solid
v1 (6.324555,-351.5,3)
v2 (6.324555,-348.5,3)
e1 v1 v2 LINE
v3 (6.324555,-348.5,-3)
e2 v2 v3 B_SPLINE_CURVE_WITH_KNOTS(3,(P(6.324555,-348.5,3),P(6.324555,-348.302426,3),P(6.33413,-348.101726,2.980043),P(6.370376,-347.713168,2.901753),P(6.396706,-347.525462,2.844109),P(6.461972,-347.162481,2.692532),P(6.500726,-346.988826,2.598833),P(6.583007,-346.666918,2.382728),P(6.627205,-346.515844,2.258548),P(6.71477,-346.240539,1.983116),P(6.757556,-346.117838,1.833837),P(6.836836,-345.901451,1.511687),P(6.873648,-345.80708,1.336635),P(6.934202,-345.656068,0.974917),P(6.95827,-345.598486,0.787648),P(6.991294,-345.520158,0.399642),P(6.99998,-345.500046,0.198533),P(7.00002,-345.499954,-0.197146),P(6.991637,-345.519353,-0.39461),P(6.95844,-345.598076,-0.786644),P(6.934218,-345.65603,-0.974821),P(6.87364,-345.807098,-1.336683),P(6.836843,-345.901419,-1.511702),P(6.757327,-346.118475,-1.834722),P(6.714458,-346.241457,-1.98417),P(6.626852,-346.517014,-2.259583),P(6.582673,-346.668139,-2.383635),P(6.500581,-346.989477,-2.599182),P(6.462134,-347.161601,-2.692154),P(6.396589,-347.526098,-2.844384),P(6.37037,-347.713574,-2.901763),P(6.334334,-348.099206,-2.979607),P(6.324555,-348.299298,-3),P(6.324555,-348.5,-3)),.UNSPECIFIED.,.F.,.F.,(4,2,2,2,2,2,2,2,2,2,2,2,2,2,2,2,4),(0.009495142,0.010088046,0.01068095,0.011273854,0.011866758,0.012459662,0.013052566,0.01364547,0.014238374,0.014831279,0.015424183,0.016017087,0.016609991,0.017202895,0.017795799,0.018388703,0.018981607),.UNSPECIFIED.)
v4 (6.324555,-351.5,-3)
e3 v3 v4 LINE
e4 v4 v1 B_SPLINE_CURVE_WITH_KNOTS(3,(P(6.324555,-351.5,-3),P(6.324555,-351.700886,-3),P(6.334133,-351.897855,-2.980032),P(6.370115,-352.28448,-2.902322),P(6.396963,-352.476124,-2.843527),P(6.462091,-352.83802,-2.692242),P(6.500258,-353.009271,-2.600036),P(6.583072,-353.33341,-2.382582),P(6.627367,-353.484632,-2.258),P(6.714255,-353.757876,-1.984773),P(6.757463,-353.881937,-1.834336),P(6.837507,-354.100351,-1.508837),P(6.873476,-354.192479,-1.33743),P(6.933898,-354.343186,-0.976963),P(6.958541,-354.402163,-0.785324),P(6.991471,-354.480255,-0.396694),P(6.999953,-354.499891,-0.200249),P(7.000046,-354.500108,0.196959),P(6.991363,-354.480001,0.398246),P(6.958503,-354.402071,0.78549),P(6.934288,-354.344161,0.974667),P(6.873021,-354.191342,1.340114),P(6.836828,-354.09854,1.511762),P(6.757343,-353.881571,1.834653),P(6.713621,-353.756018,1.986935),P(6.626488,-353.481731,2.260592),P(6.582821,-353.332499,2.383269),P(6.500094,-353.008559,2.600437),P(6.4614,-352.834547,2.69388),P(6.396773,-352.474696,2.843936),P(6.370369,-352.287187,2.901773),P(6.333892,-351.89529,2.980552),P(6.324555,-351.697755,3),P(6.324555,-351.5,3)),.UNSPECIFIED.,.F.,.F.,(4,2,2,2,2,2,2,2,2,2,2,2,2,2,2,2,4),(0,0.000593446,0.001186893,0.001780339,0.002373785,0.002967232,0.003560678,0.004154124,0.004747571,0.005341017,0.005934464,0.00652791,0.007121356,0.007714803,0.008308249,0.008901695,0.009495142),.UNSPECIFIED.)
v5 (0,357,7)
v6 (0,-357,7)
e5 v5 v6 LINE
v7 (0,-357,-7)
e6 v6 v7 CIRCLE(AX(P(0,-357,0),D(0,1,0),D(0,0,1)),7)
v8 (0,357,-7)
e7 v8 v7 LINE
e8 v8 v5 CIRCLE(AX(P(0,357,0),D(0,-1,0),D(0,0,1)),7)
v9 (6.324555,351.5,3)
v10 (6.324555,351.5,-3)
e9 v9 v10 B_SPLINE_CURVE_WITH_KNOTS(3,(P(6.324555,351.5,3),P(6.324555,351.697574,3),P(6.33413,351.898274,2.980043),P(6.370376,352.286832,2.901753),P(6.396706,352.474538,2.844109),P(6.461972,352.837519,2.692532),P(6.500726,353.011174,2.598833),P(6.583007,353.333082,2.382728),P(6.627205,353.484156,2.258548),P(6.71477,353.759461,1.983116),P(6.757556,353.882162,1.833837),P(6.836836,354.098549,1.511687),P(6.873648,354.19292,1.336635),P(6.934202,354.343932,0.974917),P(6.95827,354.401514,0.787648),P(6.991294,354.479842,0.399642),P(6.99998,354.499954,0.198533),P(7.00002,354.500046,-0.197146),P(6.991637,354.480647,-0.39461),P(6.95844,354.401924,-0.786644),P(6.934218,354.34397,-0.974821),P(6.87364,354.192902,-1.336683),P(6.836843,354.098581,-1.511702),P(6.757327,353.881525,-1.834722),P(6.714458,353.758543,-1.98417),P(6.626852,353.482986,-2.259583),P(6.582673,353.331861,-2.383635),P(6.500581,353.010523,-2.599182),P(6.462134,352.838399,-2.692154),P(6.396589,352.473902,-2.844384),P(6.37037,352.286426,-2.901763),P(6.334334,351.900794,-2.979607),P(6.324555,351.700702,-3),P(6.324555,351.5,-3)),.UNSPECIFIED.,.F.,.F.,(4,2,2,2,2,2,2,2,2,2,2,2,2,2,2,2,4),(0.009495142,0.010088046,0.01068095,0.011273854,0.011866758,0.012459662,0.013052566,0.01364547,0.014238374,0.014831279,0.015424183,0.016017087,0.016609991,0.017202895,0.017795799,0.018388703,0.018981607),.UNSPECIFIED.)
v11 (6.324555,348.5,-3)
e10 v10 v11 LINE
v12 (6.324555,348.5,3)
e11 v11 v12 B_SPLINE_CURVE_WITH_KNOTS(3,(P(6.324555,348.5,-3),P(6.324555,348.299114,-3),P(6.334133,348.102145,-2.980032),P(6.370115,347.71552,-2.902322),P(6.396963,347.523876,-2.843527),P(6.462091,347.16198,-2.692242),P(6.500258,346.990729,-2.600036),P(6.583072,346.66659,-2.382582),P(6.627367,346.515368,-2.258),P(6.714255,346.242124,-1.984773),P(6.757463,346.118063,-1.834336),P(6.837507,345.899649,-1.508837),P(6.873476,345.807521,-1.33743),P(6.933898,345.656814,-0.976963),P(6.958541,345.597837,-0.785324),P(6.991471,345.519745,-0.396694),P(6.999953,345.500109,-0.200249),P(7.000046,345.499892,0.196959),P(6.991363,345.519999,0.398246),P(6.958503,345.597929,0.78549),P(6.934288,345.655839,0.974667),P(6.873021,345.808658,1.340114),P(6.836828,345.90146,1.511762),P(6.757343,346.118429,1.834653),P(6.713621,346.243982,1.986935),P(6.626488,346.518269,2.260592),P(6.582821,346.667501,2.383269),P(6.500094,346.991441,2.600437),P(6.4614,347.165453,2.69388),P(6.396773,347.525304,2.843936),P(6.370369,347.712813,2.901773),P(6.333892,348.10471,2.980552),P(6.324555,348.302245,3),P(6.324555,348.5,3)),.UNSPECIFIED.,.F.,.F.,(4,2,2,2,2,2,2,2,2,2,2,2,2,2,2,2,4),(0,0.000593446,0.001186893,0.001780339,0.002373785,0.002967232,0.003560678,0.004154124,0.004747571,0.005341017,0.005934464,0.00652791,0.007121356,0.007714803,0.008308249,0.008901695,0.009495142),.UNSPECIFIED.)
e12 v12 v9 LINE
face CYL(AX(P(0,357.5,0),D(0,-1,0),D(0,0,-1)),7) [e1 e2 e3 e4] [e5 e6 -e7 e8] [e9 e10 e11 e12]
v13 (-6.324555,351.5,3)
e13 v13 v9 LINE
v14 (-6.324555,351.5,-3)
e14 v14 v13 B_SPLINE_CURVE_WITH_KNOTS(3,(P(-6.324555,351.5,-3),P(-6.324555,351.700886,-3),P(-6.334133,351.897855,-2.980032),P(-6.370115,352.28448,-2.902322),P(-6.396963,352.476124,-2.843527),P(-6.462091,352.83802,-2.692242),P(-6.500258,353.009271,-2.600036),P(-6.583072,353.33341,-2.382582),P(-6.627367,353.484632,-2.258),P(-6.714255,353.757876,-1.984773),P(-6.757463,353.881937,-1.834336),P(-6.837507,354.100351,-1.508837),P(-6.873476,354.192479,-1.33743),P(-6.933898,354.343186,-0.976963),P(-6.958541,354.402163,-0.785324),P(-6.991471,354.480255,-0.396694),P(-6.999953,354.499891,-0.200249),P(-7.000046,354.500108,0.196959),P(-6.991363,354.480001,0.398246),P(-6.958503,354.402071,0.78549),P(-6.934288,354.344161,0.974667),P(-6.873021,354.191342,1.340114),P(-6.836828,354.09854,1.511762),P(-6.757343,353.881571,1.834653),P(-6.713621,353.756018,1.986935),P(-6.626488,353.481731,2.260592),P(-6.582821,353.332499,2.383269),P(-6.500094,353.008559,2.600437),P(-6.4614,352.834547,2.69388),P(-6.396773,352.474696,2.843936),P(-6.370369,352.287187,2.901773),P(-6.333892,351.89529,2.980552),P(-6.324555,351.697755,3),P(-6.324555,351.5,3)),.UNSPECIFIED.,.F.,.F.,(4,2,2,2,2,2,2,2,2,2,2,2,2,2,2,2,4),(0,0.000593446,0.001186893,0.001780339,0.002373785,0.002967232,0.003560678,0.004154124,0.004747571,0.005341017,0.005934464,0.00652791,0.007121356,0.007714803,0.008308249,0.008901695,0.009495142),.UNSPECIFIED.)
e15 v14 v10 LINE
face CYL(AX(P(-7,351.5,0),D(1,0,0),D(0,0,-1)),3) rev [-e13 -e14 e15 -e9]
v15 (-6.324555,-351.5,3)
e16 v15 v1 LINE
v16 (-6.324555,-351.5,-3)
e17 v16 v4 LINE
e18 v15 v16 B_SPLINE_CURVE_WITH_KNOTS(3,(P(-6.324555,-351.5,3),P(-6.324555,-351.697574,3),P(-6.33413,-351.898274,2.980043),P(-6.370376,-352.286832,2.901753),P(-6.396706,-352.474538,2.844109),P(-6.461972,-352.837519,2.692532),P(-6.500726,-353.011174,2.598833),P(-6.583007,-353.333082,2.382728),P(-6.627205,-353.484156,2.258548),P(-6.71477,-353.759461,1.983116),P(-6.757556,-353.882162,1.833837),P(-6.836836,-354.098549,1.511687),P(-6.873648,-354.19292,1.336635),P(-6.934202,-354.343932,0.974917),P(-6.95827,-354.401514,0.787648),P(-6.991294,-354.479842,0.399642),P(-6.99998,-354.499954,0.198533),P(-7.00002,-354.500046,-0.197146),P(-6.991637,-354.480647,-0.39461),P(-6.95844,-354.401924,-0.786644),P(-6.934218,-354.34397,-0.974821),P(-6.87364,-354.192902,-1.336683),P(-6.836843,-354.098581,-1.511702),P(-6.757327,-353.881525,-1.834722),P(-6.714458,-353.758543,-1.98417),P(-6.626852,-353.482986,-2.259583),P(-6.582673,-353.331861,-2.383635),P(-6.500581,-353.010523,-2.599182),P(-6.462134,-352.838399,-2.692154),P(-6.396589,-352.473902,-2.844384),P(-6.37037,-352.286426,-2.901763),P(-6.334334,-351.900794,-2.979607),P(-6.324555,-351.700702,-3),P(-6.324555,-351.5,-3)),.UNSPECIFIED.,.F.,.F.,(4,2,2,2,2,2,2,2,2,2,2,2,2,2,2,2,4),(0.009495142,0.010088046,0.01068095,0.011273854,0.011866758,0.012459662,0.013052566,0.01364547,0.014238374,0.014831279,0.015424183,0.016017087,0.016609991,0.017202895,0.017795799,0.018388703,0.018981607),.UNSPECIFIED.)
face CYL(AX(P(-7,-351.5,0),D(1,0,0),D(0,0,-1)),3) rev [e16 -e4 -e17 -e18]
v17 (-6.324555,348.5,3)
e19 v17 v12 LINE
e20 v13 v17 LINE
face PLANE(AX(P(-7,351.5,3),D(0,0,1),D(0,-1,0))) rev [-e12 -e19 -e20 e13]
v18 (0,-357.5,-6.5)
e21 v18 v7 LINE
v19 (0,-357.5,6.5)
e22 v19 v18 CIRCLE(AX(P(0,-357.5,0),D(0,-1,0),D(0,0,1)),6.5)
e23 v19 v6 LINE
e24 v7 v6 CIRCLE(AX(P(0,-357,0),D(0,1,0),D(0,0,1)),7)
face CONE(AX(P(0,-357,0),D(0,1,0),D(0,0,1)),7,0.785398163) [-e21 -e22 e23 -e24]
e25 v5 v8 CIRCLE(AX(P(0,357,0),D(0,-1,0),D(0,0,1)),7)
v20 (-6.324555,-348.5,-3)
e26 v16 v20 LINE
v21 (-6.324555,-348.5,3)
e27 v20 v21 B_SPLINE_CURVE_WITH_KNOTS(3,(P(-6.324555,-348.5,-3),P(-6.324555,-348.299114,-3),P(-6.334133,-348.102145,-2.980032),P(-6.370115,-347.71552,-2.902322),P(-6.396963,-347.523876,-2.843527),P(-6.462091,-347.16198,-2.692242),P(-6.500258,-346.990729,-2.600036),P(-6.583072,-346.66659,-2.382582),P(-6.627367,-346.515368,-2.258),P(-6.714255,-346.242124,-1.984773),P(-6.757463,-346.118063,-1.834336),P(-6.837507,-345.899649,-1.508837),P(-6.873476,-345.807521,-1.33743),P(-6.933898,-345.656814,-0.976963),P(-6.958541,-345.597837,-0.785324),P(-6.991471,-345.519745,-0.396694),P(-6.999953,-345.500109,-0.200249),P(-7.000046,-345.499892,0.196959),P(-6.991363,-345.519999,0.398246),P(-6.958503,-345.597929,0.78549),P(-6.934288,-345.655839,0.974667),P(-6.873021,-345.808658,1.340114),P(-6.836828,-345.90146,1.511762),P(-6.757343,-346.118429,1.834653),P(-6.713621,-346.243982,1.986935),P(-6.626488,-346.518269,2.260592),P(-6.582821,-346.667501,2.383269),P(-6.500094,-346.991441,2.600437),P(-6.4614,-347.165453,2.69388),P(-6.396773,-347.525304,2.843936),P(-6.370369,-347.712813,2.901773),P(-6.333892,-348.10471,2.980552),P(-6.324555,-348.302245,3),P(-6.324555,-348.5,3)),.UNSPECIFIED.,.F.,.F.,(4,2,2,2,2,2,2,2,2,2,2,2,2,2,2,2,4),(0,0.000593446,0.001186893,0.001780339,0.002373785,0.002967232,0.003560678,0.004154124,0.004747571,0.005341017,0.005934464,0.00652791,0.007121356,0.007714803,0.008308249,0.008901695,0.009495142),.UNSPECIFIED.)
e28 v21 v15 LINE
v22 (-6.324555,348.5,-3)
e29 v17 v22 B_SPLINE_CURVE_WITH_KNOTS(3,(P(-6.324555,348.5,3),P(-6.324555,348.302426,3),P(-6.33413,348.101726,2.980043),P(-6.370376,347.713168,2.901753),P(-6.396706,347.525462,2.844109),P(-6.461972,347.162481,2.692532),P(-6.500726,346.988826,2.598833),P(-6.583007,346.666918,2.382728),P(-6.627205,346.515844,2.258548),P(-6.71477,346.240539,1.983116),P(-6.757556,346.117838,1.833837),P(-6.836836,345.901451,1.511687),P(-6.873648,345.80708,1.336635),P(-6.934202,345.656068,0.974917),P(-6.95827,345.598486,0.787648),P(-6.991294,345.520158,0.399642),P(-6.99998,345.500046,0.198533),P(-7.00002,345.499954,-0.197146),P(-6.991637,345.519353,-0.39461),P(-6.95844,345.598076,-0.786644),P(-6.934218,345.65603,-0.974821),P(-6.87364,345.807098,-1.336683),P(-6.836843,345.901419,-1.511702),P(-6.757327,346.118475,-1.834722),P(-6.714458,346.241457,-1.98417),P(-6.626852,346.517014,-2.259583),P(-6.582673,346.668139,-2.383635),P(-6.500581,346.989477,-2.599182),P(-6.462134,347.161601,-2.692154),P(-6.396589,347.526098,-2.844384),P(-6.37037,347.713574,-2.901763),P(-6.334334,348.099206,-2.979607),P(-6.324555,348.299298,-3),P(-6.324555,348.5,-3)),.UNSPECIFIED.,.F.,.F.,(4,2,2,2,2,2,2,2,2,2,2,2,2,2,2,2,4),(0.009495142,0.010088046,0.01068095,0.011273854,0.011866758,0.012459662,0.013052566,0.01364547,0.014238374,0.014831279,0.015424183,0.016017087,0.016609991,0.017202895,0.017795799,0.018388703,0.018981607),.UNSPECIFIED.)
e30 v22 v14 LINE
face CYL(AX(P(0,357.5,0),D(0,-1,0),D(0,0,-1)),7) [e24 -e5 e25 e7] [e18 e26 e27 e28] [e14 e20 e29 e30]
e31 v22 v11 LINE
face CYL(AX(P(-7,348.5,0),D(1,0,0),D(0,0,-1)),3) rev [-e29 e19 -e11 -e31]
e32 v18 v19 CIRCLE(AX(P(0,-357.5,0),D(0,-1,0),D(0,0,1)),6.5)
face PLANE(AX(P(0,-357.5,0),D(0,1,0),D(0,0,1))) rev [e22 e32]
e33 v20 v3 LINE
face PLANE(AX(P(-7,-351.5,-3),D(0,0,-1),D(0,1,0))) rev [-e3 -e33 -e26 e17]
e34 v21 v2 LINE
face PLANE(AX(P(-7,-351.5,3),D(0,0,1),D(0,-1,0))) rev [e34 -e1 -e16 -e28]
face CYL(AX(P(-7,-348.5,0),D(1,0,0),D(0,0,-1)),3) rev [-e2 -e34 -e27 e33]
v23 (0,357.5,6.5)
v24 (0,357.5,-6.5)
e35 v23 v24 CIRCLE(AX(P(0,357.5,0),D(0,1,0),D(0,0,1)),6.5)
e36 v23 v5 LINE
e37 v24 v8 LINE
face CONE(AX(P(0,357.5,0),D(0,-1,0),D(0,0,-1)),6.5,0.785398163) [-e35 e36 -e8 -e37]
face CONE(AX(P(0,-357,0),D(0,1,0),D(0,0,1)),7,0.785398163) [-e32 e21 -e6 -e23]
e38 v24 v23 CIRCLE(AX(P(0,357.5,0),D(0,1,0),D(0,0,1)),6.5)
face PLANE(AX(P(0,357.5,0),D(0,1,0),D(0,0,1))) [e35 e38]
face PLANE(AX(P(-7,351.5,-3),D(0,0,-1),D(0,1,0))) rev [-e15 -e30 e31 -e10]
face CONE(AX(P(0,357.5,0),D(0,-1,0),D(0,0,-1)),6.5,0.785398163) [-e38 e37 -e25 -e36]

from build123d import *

# Parameters (mm, degrees)
SKETCH_1_R               = 7
EXTRUDE_1_DEPTH          = 357.5
CHAMFER_1_SIZE           = 0.5
CUT_EXTRUDE_1_DEPTH      = 358.637036673
CUT_EXTRUDE_1_DEPTH_BACK = 358.637036673


with BuildPart() as part:
    # 草图1 → 凸台-拉伸1 (new, symmetric)
    with BuildSketch(Plane(origin=(0, 0, 0), x_dir=(1, 0, 0), z_dir=(0, 1, 0))):
        with Locations(Location((0, 0, 0), (0, 0, 270))):
            Circle(SKETCH_1_R)
    extrude(amount=EXTRUDE_1_DEPTH, both=True)

    # 倒角1
    chamfer_1_edges = [part.edges().sort_by_distance(p)[0] for p in [
        (0, -357.5, -7),
        (0, 357.5, -7),
    ]]
    chamfer(chamfer_1_edges, length=CHAMFER_1_SIZE)

    # 草图2 → 切除-拉伸1 (cut, two sides: drawn at the far end of the back side and taken through both)
    with BuildSketch(Plane(origin=(0, 0, 0), x_dir=(0, 0, -1), z_dir=(1, 0, 0)).offset(-CUT_EXTRUDE_1_DEPTH_BACK)):
        with BuildLine():
            Line((-3, -351.5), (-3, -348.5))
            ThreePointArc((-3, -348.5), (0, -345.5), (3, -348.5))
            Line((3, -348.5), (3, -351.5))
            ThreePointArc((3, -351.5), (0, -354.5), (-3, -351.5))
        make_face()
        with BuildLine():
            Line((-3, 351.5), (-3, 348.5))
            ThreePointArc((-3, 348.5), (0, 345.5), (3, 348.5))
            Line((3, 348.5), (3, 351.5))
            ThreePointArc((3, 351.5), (0, 354.5), (-3, 351.5))
        make_face()
    extrude(amount=CUT_EXTRUDE_1_DEPTH + CUT_EXTRUDE_1_DEPTH_BACK, mode=Mode.SUBTRACT)


solid = part.part
